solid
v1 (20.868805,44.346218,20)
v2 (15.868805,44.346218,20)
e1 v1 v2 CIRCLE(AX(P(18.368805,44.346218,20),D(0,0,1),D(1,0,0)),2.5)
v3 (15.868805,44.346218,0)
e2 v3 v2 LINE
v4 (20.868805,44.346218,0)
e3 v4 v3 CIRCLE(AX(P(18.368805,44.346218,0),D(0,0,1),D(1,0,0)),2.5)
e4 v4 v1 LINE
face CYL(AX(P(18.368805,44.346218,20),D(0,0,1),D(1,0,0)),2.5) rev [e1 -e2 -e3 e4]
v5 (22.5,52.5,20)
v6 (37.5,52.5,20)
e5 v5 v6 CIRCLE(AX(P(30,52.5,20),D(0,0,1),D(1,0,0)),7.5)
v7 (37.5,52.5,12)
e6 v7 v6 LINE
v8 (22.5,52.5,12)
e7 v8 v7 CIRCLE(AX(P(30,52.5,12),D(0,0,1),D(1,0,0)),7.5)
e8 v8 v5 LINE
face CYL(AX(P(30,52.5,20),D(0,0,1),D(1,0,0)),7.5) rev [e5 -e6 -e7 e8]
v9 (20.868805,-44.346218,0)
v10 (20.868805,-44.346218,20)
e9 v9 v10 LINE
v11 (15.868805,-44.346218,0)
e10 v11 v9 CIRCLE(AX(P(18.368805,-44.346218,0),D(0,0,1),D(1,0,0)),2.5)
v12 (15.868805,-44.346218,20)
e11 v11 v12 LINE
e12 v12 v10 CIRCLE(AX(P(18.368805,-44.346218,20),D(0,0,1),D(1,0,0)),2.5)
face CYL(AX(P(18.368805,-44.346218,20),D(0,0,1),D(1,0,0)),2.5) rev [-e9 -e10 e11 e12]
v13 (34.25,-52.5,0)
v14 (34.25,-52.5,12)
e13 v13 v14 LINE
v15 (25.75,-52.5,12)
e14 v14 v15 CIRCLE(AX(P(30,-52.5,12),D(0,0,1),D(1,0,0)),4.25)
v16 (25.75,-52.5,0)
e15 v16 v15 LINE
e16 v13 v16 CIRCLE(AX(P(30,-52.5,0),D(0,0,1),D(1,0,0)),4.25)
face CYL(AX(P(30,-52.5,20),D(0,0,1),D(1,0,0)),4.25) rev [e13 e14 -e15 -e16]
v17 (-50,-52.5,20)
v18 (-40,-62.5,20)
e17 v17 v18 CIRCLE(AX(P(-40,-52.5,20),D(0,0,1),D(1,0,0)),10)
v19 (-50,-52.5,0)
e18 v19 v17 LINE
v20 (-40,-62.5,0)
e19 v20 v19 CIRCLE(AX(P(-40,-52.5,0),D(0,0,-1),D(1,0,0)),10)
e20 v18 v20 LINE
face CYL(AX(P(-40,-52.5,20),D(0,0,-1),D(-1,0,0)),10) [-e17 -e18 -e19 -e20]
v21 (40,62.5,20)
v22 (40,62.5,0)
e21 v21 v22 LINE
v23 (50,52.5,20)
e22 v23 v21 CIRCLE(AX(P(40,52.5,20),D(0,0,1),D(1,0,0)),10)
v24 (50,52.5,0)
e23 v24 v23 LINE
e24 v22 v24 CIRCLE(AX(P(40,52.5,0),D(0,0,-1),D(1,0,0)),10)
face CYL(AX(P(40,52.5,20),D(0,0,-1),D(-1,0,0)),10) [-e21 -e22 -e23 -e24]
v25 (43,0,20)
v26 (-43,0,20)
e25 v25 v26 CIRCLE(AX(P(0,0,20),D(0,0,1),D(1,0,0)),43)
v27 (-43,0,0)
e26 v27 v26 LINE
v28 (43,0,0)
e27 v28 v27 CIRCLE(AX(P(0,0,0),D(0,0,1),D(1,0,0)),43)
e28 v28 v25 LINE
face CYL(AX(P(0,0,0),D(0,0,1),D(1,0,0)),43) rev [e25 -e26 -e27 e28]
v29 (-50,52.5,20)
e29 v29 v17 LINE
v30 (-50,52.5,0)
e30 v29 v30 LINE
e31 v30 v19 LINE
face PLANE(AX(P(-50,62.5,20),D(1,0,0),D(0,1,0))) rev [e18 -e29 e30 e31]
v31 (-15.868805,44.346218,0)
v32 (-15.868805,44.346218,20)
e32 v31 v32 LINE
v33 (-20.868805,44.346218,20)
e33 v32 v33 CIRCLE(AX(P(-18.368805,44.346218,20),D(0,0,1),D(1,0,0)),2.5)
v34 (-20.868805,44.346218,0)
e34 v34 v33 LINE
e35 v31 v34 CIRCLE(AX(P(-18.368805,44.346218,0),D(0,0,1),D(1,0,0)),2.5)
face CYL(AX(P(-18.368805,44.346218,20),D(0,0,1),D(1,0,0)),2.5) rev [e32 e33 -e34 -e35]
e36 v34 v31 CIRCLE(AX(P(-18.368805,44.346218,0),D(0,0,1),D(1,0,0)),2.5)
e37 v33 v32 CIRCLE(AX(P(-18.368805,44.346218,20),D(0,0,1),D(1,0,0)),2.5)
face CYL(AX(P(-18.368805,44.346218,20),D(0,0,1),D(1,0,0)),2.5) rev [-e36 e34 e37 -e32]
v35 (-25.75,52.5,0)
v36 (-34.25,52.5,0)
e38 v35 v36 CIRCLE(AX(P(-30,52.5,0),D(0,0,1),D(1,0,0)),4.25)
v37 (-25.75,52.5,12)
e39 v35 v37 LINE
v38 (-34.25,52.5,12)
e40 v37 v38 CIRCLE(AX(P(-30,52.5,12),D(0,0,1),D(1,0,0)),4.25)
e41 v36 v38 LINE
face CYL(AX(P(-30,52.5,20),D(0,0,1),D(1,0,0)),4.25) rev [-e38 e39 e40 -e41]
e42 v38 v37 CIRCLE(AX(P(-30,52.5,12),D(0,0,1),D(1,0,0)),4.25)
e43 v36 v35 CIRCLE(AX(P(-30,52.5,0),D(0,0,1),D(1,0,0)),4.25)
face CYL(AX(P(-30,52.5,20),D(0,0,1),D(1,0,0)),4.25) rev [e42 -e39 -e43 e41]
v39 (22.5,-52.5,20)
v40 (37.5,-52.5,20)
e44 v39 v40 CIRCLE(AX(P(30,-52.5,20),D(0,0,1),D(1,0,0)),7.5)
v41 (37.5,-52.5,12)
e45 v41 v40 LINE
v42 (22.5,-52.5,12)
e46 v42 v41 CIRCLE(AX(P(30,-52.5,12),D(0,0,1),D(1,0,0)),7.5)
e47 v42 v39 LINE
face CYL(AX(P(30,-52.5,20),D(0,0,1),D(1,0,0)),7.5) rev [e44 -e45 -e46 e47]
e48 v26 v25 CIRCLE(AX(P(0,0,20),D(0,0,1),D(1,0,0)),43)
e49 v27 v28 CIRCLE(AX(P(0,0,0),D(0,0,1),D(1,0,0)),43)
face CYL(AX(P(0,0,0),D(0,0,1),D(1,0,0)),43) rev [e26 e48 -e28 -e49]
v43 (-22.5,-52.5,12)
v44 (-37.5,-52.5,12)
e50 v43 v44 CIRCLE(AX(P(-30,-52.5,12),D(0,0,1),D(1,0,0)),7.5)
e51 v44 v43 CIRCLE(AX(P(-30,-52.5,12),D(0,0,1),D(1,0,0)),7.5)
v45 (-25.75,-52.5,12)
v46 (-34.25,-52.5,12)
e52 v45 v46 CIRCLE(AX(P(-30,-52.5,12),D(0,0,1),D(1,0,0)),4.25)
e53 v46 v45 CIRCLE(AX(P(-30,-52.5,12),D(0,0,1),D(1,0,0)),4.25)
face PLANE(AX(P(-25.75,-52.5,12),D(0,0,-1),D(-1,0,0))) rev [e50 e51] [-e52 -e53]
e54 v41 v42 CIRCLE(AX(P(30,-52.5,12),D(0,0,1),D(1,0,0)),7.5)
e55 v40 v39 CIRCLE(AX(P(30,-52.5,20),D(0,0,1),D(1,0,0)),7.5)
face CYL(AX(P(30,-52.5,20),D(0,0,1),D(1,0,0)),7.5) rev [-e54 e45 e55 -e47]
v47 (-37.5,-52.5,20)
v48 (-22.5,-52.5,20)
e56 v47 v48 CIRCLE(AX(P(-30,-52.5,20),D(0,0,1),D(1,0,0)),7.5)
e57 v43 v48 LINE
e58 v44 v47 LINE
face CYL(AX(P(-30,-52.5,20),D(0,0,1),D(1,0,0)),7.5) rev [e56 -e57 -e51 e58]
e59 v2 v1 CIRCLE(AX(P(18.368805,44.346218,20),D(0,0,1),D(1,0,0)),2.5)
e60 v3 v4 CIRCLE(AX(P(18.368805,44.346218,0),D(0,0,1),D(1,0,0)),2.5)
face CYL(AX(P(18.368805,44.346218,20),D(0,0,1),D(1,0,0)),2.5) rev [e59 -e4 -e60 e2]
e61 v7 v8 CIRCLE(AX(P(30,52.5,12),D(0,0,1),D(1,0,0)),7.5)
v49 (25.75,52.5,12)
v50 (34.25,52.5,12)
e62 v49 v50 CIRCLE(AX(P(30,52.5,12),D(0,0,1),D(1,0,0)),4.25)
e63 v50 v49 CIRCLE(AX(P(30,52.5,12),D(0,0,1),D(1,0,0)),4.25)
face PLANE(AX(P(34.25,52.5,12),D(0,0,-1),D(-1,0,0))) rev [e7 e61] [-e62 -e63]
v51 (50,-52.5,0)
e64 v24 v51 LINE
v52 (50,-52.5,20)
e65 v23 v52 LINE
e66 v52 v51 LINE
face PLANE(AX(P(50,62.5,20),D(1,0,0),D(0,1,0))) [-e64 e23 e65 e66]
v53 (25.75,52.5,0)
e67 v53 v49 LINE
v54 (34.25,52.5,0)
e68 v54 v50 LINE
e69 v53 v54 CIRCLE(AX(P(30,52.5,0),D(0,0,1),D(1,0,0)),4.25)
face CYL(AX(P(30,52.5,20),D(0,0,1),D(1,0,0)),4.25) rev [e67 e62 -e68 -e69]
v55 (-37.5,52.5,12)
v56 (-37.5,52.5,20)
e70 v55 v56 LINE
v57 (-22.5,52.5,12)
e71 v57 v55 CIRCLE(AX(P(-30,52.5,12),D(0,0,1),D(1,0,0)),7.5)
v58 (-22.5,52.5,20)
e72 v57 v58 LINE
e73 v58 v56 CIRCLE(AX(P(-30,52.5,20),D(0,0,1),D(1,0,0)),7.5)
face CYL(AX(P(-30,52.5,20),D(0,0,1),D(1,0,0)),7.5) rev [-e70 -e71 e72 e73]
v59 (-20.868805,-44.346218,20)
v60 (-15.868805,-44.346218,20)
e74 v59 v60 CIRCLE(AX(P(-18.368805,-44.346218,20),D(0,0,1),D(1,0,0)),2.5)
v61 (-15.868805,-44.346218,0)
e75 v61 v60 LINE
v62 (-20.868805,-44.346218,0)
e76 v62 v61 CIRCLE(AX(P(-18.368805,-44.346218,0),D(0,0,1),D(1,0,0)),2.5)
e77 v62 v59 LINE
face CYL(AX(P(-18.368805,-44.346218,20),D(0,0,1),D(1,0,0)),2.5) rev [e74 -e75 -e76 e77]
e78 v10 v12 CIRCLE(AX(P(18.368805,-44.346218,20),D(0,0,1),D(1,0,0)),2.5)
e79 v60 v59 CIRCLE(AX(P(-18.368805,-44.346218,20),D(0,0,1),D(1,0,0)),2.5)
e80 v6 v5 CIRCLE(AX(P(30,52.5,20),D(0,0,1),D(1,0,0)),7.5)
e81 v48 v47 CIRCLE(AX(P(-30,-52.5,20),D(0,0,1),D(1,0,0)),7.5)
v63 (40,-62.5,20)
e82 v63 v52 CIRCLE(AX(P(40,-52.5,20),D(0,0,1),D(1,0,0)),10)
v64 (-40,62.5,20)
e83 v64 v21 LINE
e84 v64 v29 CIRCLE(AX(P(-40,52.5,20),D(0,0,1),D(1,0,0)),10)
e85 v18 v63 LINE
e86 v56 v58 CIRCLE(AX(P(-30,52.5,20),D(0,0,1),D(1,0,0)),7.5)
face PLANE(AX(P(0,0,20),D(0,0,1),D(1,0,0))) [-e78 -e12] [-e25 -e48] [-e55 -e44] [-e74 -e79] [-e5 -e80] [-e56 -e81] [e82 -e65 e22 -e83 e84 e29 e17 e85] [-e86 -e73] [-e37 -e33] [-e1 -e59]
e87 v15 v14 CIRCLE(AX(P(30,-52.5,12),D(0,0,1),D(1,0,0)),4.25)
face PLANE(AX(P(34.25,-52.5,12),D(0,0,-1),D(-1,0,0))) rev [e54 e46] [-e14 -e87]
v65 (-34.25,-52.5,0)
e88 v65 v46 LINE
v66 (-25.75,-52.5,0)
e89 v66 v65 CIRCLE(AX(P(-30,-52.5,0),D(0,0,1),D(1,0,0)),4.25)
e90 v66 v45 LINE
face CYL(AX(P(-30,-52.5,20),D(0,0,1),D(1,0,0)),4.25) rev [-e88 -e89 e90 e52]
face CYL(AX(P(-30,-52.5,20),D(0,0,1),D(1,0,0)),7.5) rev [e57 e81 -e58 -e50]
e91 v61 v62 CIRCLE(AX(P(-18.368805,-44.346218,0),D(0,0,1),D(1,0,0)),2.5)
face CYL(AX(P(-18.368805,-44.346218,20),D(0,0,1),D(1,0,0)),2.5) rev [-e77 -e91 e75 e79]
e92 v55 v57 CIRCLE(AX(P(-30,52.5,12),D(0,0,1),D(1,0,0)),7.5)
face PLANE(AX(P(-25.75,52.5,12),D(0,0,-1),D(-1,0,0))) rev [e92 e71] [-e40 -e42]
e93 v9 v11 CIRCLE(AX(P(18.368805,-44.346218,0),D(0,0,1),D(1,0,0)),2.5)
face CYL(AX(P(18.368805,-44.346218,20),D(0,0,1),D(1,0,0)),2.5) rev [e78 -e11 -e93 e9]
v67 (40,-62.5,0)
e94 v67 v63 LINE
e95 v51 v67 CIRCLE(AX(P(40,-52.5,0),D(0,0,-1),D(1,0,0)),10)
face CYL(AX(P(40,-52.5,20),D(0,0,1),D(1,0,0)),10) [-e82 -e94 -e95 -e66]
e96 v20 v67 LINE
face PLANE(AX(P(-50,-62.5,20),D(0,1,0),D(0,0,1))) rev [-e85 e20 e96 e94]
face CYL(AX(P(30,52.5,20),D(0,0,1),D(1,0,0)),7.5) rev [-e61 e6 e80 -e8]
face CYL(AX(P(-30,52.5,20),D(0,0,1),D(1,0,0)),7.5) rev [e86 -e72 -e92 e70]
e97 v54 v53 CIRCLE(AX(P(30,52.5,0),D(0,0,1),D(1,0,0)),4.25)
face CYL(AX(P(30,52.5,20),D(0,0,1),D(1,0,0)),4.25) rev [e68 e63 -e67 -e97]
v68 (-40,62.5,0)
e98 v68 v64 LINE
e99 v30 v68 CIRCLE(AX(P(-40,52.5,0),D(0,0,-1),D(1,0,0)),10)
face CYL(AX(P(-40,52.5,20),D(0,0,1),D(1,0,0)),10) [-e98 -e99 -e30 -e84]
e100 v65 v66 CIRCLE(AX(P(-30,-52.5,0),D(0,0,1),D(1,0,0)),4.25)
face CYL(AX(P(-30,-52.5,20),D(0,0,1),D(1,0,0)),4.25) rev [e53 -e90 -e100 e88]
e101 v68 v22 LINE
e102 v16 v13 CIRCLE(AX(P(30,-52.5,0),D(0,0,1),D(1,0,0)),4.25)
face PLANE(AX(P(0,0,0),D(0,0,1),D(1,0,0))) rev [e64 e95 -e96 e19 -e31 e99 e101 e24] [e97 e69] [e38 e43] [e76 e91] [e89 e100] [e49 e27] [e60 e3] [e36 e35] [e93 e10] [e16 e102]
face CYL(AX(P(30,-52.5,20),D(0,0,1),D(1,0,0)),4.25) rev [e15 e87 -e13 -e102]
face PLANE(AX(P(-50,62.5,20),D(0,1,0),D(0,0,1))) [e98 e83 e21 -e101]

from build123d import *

# Parameters (mm, degrees)
SKETCH_1_W                   = 100
SKETCH_1_H                   = 125
EXTRUDE_1_DEPTH              = 20
HOLE_WIZARD_M8_1_D           = 8.5
HOLE_WIZARD_M8_1_CBORE_D     = 15
HOLE_WIZARD_M8_1_CBORE_DEPTH = 8
SKETCH_4_R                   = 43
CUT_EXTRUDE_1_DEPTH          = 83.5
HOLE_WIZARD_M6_1_D           = 5
FILLET_1_R                   = 10


with BuildPart() as part:
    # 草图1 → 凸台-拉伸1 (new body)
    with BuildSketch(Plane.XY):
        Rectangle(SKETCH_1_W, SKETCH_1_H)
    extrude(amount=EXTRUDE_1_DEPTH)

    # M8 六角凹头螺钉的柱形沉头孔1 (through all)
    with Locations(Plane.XY.offset(20)):
        with Locations((-30, -52.5), (30, -52.5)):
            hole_wizard_m8_1 = CounterBoreHole(HOLE_WIZARD_M8_1_D / 2, HOLE_WIZARD_M8_1_CBORE_D / 2, HOLE_WIZARD_M8_1_CBORE_DEPTH)

    # 草图4 → 切除-拉伸1 (cut, through all)
    with BuildSketch(Plane.XY.offset(20)):
        Circle(SKETCH_4_R)
    extrude(amount=-CUT_EXTRUDE_1_DEPTH, mode=Mode.SUBTRACT)

    # M6 螺纹孔1 (through all)
    with Locations(Plane.XY.offset(20)):
        with Locations((-18.368804754, 44.346217561), (18.368804754, 44.346217561)):
            hole_wizard_m6_1 = Hole(HOLE_WIZARD_M6_1_D / 2)

    # 镜向2: M8 六角凹头螺钉的柱形沉头孔1, M6 螺纹孔1 across plane
    add(hole_wizard_m8_1.mirror(Plane.ZX), mode=Mode.SUBTRACT)
    add(hole_wizard_m6_1.mirror(Plane.ZX), mode=Mode.SUBTRACT)

    # 圆角1
    fillet_1_edges = [part.edges().sort_by_distance(p)[0] for p in [
        (-50, 62.5, 10),
        (50, 62.5, 10),
        (50, -62.5, 10),
        (-50, -62.5, 10),
    ]]
    fillet(fillet_1_edges, radius=FILLET_1_R)


solid = part.part
